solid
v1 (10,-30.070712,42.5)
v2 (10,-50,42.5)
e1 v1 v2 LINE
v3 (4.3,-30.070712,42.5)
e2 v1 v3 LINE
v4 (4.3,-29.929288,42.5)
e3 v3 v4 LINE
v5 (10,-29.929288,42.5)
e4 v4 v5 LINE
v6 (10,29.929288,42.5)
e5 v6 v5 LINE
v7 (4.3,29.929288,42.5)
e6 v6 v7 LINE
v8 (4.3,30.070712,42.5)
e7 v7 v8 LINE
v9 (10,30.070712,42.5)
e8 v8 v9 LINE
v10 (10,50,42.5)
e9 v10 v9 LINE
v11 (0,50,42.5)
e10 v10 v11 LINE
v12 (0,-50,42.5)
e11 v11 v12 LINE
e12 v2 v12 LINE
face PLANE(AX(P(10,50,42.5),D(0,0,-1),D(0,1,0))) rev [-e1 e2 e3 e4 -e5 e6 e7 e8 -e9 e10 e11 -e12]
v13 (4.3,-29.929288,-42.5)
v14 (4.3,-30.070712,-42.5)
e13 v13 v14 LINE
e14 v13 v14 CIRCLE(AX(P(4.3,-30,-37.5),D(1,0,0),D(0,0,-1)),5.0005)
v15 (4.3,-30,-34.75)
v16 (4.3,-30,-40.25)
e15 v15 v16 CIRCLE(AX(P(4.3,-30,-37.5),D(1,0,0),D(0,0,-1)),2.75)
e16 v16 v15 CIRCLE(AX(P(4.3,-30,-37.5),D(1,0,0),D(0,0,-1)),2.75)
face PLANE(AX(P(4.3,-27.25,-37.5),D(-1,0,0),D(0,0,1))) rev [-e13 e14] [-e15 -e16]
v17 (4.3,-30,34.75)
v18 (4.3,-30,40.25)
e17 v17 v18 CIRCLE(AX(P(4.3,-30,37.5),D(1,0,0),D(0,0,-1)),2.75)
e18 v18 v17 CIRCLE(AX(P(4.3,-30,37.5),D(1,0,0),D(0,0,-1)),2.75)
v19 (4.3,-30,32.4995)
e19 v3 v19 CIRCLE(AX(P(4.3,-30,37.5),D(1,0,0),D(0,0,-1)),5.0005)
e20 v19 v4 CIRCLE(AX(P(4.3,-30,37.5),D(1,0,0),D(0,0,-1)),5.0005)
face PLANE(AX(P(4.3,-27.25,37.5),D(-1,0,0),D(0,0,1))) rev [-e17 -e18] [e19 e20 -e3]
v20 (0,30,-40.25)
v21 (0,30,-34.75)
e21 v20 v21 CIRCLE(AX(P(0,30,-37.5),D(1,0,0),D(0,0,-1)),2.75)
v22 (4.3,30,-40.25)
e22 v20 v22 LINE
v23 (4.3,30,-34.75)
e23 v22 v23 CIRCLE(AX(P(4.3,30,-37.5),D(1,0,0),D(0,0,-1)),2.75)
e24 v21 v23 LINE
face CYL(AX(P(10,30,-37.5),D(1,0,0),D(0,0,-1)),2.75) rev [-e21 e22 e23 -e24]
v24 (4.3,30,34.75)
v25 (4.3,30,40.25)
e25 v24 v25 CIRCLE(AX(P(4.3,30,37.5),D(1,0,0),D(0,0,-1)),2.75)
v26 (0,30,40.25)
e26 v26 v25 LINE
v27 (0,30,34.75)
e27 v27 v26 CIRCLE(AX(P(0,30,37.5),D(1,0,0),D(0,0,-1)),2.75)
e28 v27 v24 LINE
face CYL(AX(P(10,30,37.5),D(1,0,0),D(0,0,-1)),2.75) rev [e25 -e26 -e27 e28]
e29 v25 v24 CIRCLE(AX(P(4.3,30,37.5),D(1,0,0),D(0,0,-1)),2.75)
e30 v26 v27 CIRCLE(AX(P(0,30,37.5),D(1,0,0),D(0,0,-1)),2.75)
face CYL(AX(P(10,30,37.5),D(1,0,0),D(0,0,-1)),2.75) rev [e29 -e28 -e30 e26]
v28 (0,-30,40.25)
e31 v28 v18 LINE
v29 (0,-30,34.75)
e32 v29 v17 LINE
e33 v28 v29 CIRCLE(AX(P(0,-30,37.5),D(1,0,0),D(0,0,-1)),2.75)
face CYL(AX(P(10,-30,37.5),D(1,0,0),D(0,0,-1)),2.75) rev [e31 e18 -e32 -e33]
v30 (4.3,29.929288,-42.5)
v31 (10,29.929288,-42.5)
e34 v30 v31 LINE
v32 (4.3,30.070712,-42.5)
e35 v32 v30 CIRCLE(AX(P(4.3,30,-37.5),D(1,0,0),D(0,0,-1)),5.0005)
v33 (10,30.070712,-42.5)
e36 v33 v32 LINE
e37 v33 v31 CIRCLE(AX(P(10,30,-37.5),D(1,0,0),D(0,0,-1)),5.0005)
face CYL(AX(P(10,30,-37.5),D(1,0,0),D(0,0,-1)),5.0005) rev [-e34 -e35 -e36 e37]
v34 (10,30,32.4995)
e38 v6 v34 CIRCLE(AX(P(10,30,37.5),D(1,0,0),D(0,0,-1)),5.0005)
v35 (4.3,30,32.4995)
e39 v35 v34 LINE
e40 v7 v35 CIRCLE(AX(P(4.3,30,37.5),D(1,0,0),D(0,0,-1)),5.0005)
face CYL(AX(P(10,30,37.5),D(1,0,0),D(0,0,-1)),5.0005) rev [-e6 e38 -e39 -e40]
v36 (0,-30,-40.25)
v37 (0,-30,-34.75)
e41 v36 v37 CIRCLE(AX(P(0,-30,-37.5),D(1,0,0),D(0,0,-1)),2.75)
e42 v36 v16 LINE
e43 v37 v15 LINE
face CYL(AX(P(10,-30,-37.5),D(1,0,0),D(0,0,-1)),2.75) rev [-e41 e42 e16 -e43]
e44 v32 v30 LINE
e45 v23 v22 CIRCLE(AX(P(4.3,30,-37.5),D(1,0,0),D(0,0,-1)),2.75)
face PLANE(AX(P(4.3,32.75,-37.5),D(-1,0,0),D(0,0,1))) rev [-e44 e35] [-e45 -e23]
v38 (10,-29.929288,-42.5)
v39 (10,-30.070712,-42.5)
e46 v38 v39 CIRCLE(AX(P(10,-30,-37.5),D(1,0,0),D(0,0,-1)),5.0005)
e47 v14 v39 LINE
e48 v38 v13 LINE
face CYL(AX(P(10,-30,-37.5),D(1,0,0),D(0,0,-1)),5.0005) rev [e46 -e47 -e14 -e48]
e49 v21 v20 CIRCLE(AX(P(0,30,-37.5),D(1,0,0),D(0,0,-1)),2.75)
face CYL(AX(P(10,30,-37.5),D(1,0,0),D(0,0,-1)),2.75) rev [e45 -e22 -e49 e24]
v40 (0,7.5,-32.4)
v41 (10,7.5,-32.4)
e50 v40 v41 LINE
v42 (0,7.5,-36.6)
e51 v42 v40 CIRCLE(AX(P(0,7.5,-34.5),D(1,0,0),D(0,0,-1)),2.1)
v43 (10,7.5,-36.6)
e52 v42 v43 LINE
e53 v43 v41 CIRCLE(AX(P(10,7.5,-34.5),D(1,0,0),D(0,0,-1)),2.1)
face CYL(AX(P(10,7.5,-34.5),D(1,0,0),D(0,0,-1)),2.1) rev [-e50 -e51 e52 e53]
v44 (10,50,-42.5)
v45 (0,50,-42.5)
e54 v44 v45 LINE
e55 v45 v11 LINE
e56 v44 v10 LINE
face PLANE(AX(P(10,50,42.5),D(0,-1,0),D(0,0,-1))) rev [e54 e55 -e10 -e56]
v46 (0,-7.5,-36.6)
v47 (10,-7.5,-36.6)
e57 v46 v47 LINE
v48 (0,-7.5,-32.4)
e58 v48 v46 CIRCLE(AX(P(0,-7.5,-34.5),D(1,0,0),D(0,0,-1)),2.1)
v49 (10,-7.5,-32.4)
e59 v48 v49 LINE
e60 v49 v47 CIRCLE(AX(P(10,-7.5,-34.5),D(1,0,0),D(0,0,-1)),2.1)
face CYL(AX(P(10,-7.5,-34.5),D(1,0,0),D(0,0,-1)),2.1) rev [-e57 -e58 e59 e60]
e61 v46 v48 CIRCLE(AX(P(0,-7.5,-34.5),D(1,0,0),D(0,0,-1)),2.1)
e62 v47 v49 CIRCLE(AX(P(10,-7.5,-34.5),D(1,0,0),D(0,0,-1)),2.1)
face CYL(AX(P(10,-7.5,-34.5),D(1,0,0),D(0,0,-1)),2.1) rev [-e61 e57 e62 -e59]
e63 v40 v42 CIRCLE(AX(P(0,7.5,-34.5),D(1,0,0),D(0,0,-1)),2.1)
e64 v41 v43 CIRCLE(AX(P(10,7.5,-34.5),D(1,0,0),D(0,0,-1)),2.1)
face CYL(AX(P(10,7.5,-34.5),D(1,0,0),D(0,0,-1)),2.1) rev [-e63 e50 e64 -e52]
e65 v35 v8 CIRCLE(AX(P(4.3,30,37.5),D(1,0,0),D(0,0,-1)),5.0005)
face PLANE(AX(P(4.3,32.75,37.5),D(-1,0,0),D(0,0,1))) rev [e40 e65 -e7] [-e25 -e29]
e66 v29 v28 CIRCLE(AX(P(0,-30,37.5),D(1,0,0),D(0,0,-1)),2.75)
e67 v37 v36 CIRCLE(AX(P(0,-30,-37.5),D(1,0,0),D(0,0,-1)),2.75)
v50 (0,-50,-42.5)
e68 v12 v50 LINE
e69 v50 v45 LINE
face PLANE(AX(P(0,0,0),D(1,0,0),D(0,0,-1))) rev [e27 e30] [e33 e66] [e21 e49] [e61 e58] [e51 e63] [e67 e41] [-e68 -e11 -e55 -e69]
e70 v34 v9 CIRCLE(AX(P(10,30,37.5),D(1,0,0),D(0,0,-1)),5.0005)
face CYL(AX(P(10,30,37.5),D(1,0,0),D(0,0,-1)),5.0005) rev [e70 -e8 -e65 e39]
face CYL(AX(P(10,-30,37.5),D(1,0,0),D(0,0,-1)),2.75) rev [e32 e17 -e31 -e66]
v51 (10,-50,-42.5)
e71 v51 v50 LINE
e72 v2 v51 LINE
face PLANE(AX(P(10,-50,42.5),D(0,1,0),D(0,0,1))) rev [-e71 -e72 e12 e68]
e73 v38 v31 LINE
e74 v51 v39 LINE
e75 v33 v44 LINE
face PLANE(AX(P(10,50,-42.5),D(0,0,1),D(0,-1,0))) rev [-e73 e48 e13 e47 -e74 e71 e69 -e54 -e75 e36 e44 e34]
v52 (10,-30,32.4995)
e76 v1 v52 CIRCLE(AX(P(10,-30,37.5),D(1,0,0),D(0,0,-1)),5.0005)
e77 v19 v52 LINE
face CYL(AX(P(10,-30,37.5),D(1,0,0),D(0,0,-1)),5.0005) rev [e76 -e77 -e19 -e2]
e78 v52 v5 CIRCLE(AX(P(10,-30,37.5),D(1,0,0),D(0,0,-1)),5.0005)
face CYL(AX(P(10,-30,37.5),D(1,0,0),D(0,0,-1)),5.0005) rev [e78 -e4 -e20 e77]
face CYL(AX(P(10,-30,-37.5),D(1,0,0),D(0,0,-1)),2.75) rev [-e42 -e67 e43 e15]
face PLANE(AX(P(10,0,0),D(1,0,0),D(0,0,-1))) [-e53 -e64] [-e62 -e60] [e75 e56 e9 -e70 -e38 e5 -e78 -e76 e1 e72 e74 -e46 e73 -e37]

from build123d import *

# Parameters (mm, degrees)
SKETCH_1_W                = 85
SKETCH_1_H                = 100
EXTRUDE_1_DEPTH           = 10
HOLE_WIZARD_1_D           = 5.5
HOLE_WIZARD_1_CBORE_D     = 10.001
HOLE_WIZARD_1_CBORE_DEPTH = 5.7
HOLE_WIZARD_M5_1_D        = 4.2


with BuildPart() as part:
    # 草图1 → 凸台-拉伸1 (new body)
    with BuildSketch(Plane(origin=(0, 0, 0), x_dir=(0, 0, -1), z_dir=(1, 0, 0))):
        Rectangle(SKETCH_1_W, SKETCH_1_H)
    extrude(amount=EXTRUDE_1_DEPTH)

    # 打孔尺寸(%根据)内六角圆柱头螺钉的类型1 (through all)
    with Locations(Plane(origin=(10, 0, 0), x_dir=(0, 0, -1), z_dir=(1, 0, 0))):
        with Locations((-37.5, 30), (-37.5, -30), (37.5, 30), (37.5, -30)):
            CounterBoreHole(HOLE_WIZARD_1_D / 2, HOLE_WIZARD_1_CBORE_D / 2, HOLE_WIZARD_1_CBORE_DEPTH)

    # M5 螺纹孔1 (through all)
    with Locations(Plane(origin=(10, 0, 0), x_dir=(0, 0, -1), z_dir=(1, 0, 0))):
        with Locations((34.5, 7.5), (34.5, -7.5)):
            Hole(HOLE_WIZARD_M5_1_D / 2)


solid = part.part
